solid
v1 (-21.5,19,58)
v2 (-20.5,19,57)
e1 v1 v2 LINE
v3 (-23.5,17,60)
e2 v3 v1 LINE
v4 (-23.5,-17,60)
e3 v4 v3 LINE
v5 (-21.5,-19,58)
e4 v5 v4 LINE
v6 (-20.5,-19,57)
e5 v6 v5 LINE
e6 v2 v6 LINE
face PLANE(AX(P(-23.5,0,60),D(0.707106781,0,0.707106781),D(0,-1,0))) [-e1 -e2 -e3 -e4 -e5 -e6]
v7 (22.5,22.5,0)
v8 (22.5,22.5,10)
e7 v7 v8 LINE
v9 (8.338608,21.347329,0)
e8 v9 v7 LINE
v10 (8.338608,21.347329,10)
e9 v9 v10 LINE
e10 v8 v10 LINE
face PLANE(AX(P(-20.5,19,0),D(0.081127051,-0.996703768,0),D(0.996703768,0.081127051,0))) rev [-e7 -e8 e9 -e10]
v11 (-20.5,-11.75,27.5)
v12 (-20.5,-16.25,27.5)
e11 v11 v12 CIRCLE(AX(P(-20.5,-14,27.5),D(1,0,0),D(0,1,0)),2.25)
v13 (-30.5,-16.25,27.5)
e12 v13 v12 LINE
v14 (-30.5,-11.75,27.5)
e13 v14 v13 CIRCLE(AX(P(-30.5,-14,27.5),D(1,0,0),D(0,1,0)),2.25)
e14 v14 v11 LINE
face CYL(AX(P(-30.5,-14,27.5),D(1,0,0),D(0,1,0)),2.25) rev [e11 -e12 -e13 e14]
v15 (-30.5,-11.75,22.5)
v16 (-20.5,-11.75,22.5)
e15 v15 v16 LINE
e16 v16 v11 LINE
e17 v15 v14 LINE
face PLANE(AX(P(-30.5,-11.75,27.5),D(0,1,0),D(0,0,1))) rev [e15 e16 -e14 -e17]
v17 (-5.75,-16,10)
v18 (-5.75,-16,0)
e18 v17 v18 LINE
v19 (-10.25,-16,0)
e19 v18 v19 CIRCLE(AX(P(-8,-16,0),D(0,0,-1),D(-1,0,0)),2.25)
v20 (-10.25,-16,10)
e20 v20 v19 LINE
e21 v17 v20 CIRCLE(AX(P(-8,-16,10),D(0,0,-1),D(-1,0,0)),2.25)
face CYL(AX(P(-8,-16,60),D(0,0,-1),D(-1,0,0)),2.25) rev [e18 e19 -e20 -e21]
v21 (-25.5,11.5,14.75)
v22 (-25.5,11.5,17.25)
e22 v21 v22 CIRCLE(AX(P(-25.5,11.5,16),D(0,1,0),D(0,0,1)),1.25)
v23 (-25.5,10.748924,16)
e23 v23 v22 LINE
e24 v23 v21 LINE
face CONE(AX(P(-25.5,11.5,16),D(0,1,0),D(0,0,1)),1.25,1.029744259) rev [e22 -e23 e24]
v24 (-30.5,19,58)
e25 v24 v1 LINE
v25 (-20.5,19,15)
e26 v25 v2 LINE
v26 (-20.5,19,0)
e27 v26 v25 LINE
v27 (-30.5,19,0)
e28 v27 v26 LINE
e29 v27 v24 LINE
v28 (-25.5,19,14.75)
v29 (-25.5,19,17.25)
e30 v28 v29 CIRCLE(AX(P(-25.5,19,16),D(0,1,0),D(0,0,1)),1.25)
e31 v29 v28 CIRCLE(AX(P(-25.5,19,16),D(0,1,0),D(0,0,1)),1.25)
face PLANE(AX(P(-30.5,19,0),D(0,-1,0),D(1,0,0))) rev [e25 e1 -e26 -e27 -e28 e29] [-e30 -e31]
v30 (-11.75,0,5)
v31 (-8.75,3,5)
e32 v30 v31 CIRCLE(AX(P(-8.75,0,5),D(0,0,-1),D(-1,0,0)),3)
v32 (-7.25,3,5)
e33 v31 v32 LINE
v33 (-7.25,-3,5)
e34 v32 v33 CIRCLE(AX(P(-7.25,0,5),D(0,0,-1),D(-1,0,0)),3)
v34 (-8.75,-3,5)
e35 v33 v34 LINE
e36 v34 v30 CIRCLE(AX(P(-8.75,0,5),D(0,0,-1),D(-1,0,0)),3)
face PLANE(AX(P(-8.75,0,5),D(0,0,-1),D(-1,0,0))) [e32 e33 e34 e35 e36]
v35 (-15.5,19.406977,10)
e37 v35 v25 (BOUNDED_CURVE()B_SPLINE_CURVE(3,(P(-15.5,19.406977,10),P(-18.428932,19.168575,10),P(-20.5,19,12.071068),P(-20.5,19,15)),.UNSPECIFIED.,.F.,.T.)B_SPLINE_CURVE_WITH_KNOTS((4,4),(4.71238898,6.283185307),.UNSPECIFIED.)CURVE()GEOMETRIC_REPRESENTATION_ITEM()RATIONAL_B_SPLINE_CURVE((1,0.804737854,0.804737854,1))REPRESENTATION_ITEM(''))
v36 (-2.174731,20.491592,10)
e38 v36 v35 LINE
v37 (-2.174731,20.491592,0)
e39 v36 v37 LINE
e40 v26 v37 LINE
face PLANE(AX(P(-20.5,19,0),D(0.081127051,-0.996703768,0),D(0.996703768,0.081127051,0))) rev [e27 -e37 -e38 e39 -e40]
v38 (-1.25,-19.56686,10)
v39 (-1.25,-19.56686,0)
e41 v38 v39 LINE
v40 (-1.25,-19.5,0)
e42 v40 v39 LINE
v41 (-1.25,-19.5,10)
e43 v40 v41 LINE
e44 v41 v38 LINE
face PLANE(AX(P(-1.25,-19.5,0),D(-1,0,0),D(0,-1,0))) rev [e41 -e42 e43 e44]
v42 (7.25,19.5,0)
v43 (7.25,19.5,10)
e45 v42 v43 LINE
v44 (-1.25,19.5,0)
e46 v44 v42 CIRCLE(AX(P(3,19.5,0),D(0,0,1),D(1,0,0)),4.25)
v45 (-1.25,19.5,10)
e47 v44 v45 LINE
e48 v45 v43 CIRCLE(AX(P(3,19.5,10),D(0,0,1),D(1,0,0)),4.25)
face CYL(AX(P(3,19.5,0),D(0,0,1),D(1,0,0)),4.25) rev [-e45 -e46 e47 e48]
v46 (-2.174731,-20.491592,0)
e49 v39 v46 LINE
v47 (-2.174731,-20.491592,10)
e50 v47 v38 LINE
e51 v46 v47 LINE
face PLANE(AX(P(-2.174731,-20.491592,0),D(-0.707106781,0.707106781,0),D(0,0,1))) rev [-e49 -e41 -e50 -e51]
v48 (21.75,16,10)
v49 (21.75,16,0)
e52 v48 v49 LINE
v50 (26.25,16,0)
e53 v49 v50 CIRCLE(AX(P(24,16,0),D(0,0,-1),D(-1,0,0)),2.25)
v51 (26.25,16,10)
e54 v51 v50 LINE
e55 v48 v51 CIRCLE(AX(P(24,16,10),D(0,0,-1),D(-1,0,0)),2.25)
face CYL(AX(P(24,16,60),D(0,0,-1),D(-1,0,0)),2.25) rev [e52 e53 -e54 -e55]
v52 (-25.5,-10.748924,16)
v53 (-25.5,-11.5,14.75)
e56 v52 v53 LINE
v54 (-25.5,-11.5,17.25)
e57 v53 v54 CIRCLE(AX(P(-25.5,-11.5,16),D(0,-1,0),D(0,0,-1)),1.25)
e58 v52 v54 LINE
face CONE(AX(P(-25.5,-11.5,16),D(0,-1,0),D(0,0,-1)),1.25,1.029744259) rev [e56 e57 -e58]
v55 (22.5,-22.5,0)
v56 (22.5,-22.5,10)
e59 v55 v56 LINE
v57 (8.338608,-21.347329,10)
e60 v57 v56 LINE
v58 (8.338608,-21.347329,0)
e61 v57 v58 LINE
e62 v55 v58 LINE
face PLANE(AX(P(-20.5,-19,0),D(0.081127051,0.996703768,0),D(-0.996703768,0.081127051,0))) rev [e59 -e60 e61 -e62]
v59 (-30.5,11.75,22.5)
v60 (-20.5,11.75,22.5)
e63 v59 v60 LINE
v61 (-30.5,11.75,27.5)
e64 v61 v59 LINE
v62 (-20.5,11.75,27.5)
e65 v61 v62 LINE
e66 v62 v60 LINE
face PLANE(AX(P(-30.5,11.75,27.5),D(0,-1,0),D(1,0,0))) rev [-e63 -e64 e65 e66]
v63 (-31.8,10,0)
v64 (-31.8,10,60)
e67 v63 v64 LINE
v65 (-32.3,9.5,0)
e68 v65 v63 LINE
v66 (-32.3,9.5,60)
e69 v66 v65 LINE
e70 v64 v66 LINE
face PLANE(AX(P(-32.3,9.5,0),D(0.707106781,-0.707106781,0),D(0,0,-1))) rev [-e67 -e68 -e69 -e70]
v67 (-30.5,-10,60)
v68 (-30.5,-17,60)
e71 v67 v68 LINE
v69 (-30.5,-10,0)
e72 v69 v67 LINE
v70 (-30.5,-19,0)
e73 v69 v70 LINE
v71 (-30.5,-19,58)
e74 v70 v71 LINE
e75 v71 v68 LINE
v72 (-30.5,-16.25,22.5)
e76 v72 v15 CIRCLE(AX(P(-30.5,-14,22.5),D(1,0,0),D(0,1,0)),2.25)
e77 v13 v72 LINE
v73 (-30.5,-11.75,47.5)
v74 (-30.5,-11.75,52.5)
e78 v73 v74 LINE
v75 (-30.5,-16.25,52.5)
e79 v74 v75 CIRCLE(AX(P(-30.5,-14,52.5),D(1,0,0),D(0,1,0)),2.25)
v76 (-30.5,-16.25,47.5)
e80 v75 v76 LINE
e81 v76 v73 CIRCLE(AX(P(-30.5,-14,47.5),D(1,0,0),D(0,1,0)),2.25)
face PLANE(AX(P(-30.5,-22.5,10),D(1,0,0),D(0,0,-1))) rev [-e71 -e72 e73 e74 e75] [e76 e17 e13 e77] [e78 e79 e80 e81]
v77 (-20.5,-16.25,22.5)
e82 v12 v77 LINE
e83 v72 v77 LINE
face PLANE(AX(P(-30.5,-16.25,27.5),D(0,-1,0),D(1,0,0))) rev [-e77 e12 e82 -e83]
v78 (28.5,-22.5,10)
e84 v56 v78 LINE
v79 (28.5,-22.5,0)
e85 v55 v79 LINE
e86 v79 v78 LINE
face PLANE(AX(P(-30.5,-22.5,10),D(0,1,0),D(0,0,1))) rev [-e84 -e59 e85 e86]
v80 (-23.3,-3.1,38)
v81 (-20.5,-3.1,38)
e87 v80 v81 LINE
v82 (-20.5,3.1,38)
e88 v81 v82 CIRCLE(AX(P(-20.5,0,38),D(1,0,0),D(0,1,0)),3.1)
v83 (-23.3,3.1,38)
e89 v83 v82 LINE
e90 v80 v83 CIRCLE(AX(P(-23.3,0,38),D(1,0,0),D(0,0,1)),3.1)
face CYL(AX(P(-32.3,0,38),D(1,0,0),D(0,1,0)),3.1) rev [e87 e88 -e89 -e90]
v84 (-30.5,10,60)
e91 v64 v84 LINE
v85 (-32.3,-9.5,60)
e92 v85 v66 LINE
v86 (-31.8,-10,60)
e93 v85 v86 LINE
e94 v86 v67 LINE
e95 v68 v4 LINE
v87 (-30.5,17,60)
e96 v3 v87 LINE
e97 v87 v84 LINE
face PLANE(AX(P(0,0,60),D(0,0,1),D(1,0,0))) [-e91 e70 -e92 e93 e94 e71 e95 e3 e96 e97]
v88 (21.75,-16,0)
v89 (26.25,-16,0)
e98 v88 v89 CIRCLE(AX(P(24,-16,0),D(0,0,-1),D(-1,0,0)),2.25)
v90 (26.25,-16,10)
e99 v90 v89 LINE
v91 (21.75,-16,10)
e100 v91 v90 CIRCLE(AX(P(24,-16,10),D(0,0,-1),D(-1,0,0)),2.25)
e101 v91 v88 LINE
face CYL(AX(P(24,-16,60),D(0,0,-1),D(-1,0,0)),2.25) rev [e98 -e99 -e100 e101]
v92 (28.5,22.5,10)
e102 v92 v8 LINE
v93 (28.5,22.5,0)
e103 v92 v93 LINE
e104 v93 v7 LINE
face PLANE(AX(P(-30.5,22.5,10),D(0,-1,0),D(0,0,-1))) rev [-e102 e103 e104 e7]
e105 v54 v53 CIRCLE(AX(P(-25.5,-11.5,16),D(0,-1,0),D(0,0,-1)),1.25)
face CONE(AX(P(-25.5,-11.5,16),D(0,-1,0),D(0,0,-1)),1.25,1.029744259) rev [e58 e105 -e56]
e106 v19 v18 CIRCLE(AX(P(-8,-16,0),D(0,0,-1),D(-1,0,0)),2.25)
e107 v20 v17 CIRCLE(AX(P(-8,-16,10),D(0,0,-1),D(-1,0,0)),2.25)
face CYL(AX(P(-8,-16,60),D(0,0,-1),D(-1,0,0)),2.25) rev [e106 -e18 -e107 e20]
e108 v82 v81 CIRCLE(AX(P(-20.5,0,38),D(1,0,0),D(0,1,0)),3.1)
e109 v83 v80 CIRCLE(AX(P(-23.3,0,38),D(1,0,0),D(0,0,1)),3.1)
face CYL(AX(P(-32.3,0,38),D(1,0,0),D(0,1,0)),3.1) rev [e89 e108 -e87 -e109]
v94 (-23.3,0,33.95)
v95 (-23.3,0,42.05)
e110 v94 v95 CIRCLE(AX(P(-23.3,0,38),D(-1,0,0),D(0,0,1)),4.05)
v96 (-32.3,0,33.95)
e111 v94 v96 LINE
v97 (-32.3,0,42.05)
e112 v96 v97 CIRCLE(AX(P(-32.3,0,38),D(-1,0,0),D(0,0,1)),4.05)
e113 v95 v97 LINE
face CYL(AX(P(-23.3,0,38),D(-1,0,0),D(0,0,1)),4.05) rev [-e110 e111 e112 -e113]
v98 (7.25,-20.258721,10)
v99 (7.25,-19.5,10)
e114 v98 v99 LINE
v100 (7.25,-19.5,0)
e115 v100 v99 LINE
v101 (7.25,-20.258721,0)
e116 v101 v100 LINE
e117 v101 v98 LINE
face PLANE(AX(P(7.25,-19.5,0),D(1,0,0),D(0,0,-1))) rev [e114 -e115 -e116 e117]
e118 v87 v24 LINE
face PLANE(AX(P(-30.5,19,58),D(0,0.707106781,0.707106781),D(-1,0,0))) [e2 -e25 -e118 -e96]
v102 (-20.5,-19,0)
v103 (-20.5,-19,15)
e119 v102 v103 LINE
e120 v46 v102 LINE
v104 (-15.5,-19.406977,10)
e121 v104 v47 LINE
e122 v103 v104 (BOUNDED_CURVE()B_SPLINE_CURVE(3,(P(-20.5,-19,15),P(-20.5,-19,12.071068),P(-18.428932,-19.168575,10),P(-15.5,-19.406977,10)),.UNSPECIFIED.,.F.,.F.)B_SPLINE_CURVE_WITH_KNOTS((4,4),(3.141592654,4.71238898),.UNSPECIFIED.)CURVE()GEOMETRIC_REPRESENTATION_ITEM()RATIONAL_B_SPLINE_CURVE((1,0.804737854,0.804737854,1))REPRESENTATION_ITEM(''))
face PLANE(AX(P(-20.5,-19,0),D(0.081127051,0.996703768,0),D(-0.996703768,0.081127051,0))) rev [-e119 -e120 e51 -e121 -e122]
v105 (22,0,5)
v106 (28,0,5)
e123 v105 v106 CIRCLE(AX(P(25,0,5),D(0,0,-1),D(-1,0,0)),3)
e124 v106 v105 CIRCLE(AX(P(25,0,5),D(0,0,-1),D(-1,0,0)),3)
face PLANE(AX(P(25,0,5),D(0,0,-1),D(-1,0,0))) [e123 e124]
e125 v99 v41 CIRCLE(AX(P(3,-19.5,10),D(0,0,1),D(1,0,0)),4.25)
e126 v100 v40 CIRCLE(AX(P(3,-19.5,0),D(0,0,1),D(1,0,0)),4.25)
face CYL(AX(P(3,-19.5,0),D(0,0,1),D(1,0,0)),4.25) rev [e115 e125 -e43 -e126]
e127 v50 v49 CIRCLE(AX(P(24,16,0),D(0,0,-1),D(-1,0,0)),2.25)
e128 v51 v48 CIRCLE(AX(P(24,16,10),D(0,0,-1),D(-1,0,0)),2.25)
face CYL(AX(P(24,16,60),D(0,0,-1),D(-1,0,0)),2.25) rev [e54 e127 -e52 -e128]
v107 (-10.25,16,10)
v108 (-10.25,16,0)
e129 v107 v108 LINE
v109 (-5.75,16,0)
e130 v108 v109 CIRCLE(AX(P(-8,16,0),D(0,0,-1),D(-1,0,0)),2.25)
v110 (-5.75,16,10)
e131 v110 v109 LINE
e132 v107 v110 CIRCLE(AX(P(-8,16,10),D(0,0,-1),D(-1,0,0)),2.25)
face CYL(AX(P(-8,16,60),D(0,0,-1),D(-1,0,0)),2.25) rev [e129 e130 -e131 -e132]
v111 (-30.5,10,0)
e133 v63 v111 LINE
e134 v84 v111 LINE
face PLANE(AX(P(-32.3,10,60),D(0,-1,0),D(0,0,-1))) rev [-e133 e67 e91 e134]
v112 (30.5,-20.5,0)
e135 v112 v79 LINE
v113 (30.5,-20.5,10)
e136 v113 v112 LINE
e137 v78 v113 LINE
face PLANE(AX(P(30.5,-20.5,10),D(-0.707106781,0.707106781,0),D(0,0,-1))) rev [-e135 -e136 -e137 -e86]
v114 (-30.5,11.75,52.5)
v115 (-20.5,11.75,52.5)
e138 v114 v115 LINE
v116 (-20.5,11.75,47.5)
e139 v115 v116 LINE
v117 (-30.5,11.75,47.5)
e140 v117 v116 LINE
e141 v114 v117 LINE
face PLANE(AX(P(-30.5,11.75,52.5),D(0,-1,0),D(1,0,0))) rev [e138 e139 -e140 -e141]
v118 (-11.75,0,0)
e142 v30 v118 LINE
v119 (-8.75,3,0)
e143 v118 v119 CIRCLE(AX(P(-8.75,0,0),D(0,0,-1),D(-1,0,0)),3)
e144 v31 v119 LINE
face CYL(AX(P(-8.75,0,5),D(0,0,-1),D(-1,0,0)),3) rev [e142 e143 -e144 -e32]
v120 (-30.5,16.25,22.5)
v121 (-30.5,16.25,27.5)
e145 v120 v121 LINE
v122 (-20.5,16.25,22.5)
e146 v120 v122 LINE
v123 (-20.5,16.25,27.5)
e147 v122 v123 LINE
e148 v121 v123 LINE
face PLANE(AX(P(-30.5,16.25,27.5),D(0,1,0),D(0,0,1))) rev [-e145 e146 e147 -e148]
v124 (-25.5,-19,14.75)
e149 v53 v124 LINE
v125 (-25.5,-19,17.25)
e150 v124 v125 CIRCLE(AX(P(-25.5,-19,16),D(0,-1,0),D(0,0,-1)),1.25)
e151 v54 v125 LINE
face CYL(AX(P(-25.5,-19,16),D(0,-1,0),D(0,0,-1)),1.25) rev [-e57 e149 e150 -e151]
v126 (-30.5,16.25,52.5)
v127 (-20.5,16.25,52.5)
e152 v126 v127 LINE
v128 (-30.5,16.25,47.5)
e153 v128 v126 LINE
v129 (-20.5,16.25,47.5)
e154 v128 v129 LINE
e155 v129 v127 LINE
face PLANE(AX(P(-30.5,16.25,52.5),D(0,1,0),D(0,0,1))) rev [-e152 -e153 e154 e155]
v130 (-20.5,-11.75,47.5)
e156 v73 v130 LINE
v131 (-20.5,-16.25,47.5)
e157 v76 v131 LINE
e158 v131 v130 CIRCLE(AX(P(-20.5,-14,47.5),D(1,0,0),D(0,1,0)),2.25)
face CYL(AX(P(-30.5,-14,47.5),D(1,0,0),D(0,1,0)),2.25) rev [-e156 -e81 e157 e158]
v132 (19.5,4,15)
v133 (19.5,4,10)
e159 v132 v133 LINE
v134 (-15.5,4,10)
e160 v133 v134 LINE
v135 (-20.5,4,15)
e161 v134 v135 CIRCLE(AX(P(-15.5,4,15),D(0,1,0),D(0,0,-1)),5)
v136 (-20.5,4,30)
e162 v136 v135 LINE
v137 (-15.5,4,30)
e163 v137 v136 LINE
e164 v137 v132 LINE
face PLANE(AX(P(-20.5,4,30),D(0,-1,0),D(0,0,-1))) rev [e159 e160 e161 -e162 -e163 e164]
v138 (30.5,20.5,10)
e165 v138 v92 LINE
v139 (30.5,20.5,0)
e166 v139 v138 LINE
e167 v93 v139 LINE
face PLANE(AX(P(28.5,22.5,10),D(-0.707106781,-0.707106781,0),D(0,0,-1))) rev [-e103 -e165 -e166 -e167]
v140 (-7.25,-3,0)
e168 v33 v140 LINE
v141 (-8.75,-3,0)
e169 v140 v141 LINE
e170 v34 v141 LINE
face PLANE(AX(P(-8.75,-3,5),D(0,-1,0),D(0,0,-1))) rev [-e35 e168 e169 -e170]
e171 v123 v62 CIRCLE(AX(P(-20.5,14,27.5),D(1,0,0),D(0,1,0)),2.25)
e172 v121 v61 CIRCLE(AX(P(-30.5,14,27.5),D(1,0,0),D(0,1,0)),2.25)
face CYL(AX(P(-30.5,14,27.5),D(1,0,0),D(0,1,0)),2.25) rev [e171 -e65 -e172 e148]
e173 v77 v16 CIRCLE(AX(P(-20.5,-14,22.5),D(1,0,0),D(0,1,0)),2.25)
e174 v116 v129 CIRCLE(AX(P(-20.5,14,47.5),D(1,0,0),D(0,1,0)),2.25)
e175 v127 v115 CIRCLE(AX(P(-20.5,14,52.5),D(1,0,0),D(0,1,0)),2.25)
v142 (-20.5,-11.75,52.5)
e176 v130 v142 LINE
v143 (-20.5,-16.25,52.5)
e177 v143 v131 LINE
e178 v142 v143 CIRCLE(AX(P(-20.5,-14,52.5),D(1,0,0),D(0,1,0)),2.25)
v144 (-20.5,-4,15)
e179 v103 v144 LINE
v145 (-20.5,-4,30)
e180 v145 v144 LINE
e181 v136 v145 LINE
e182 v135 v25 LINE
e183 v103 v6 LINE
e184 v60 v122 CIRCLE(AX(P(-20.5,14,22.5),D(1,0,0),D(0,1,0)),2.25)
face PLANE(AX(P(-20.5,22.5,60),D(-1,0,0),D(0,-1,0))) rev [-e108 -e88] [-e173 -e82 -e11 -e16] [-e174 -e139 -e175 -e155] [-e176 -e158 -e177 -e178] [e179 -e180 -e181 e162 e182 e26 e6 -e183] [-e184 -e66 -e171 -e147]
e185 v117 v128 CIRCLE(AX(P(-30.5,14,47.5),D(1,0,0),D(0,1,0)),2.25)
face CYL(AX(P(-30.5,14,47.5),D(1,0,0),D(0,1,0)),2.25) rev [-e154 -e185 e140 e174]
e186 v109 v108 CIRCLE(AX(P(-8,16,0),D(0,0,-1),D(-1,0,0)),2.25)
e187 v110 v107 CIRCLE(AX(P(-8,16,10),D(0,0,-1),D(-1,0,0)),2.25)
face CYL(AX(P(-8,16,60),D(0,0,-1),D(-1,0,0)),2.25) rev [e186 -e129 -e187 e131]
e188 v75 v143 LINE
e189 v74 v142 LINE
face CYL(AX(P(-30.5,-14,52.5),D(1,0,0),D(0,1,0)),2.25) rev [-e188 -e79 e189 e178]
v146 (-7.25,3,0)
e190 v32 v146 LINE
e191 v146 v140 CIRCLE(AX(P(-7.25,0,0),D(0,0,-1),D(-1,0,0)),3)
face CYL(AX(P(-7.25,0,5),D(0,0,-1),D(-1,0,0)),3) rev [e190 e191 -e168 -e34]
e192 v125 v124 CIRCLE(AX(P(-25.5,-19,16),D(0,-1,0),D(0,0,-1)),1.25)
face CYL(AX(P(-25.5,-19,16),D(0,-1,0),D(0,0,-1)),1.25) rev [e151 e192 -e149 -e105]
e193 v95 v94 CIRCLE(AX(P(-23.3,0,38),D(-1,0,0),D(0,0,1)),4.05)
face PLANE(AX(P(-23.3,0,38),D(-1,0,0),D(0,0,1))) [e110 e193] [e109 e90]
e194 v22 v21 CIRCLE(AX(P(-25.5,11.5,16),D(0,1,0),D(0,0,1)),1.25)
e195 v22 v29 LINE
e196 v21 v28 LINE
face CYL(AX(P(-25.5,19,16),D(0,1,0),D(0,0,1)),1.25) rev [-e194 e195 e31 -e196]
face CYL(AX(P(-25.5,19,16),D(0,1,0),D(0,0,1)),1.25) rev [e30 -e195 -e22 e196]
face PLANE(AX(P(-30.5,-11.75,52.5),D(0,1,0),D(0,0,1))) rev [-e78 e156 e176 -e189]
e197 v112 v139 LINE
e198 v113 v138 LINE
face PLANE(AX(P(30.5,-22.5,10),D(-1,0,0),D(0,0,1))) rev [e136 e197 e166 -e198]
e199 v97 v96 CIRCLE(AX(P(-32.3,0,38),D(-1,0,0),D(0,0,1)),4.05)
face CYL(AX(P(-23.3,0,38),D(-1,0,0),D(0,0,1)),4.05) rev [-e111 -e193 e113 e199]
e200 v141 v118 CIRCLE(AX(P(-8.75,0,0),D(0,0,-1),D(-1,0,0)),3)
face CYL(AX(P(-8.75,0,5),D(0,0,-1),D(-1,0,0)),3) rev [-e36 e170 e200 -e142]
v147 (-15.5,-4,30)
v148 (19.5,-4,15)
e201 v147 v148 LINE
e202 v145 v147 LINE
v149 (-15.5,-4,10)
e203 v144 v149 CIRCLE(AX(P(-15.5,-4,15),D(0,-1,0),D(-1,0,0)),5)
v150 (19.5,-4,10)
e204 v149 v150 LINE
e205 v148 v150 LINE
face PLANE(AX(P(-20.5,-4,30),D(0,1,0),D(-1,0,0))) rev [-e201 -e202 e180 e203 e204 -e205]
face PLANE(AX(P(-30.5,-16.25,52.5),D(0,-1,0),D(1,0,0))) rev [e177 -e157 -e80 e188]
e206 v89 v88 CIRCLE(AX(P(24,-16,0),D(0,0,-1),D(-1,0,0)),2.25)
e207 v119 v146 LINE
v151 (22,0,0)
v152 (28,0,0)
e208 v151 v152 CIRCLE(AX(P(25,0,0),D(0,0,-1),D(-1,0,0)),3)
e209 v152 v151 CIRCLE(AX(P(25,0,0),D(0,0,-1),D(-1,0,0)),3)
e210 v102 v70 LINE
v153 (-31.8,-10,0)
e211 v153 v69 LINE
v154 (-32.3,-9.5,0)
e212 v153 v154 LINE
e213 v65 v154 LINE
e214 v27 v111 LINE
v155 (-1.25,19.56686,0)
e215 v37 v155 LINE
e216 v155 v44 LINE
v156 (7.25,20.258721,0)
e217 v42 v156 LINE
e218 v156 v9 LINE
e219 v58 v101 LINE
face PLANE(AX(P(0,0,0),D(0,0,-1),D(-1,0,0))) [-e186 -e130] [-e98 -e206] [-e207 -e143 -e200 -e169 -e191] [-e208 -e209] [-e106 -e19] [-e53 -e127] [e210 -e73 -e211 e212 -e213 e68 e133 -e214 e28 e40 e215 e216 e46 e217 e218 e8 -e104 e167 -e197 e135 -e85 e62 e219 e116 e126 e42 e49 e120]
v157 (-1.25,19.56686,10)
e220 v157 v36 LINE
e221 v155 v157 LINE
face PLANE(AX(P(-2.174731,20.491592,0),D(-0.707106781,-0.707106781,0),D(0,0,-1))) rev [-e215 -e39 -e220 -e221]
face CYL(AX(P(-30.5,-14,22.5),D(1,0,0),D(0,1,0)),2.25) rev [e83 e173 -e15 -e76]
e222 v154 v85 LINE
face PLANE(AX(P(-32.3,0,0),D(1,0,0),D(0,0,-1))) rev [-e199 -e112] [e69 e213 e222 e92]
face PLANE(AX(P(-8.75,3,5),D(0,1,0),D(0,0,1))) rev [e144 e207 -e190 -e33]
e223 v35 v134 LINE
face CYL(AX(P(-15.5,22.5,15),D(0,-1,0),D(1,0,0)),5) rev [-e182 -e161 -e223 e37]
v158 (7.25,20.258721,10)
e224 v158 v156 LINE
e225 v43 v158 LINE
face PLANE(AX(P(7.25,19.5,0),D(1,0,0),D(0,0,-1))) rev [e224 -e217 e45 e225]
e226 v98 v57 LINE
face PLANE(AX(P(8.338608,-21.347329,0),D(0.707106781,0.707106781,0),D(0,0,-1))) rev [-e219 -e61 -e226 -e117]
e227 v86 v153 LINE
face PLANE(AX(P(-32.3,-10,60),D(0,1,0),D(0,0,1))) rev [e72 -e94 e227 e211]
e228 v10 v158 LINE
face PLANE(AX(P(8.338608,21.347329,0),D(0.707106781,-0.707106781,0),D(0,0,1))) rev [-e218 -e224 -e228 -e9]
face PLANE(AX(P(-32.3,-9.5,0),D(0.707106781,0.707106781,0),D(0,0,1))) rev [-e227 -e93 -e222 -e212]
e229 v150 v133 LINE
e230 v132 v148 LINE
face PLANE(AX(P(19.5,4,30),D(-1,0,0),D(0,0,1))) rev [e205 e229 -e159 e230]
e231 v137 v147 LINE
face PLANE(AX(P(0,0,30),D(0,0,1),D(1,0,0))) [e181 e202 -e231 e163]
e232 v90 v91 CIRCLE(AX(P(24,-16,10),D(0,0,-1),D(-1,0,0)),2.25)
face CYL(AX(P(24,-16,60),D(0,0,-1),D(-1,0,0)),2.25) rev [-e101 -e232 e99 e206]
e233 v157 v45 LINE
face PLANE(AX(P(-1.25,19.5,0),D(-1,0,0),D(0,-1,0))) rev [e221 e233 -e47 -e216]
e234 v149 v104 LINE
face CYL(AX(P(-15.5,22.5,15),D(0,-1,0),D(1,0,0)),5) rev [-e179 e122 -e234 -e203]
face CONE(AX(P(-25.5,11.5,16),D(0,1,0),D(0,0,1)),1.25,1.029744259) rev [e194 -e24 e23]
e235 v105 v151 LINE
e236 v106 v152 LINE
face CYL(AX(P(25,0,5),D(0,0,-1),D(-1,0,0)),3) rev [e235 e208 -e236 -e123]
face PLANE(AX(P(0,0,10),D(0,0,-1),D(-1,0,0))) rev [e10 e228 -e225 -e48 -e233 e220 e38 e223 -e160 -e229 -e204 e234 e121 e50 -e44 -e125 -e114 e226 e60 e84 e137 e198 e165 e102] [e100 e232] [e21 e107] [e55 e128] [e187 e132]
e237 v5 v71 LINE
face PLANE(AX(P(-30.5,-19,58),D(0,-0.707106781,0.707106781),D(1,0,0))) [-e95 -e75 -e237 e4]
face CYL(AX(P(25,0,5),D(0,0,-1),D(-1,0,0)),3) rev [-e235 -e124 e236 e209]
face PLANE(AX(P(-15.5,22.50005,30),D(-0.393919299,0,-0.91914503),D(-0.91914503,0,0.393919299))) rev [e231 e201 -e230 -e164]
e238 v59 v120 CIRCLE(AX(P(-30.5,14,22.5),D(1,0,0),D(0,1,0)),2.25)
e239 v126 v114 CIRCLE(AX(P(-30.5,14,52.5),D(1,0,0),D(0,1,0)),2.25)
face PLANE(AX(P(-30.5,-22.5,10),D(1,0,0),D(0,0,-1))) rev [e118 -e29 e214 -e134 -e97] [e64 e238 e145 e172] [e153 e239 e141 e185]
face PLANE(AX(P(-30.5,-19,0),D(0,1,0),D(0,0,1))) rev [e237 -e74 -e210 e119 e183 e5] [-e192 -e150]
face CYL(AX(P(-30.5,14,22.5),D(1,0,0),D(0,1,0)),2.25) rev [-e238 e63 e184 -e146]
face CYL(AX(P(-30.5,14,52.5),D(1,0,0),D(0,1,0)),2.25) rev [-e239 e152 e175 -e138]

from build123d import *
from OCP.BRepFilletAPI import BRepFilletAPI_MakeChamfer

# Parameters (mm, degrees)
SKETCH1_W            = 61
SKETCH1_H            = 45
BOSS_EXTRUDE1_DEPTH  = 10
SKETCH2_W            = 10
SKETCH2_H            = 45
BOSS_EXTRUDE2_DEPTH  = 50
CUT_EXTRUDE3_DEPTH   = 82.897802168
SKETCH6_W            = 40
SKETCH6_H            = 8
BOSS_EXTRUDE3_DEPTH  = 20
CUT_EXTRUDE4_DEPTH   = 73.336021455
FILLET1_R            = 5
CUT_EXTRUDE5_DEPTH   = 71.968302784
LPATTERN2_COUNT      = 2
LPATTERN2_PITCH      = 28
LPATTERN2_COUNT_DIR2 = 2
LPATTERN2_PITCH_DIR2 = 25
SKETCH9_R            = 3
CUT_EXTRUDE6_DEPTH   = 5
SKETCH10_R           = 2.25
CUT_EXTRUDE7_DEPTH   = 71.968302784
CHAMFER1_SIZE        = 2
SKETCH4_W            = 60
SKETCH4_H            = 20
BOSS_EXTRUDE4_DEPTH  = 1.8
CHAMFER2_SIZE        = 0.5
SKETCH15_R           = 3.1
CUT_EXTRUDE8_DEPTH   = 82.897802168
SKETCH16_R           = 4.05
CUT_EXTRUDE9_DEPTH   = 9
CUT_EXTRUDE10_DEPTH  = 10
CHAMFER3_SIZE        = 1
CHAMFER3_SIZE2       = 0.927789392
CHAMFER3_SIZE2_2     = 1.092207765
CHAMFER4_SIZE        = 3


with BuildPart() as part:
    # Sketch1 → Boss-Extrude1 (new body)
    with BuildSketch(Plane.XY):
        Rectangle(SKETCH1_W, SKETCH1_H)
    extrude(amount=BOSS_EXTRUDE1_DEPTH)

    # Sketch2 → Boss-Extrude2 (add)
    with BuildSketch(Plane.XY.offset(10)):
        with Locations((-25.5, 0)):
            Rectangle(SKETCH2_W, SKETCH2_H)
    extrude(amount=BOSS_EXTRUDE2_DEPTH)

    # Sketch5 → Cut-Extrude3 (cut, through all)
    with BuildSketch(Plane(origin=(-20.5, 0, 0), x_dir=(0, 0, -1), z_dir=(1, 0, 0))):
        with BuildLine():
            Line((-52.5, -11.75), (-47.5, -11.75))
            ThreePointArc((-47.5, -11.75), (-45.25, -14), (-47.5, -16.25))
            Line((-47.5, -16.25), (-52.5, -16.25))
            ThreePointArc((-52.5, -16.25), (-54.75, -14), (-52.5, -11.75))
        make_face()
    cut_extrude3 = extrude(amount=-CUT_EXTRUDE3_DEPTH, mode=Mode.SUBTRACT)

    # Sketch6 → Boss-Extrude3 (add)
    with BuildSketch(Plane.XY.offset(10)):
        with Locations((-0.5, 0)):
            Rectangle(SKETCH6_W, SKETCH6_H)
    extrude(amount=BOSS_EXTRUDE3_DEPTH)

    # Sketch7 → Cut-Extrude4 (cut, through all)
    with BuildSketch(Plane.XZ.offset(4)):
        Polygon((19.5, 30), (-15.5, 30), (19.5, 15), align=None)
    extrude(amount=-CUT_EXTRUDE4_DEPTH, mode=Mode.SUBTRACT)

    # Fillet1
    fillet1_edges = [part.edges().sort_by_distance(p)[0] for p in [
        (-20.5, 13.25, 10),
        (-20.5, -13.25, 10),
    ]]
    fillet(fillet1_edges, radius=FILLET1_R)

    # Sketch8 → Cut-Extrude5 (cut, through all)
    with BuildSketch(Plane.XY.offset(60)):
        Polygon((-30.5, 22.5), (22.5, 22.5), (-20.5, 19), (-30.5, 19), align=None)
        Polygon((-20.5, -19), (22.5, -22.5), (-30.5, -22.5), (-30.5, -19), align=None)
    extrude(amount=-CUT_EXTRUDE5_DEPTH, mode=Mode.SUBTRACT)

    # LPattern2: Cut-Extrude3 2 × 2
    with Locations(*[(0, i * LPATTERN2_PITCH, -j * LPATTERN2_PITCH_DIR2) for i in range(LPATTERN2_COUNT) for j in range(LPATTERN2_COUNT_DIR2) if (i, j) != (0, 0)]):
        add(cut_extrude3, mode=Mode.SUBTRACT)

    # Sketch9 → Cut-Extrude6 (cut)
    with BuildSketch(Plane(origin=(0, 0, 0), x_dir=(-1, 0, 0), z_dir=(0, 0, -1))):
        with Locations((-25, 0)):
            Circle(SKETCH9_R)
        with BuildLine():
            Line((8.75, -3), (7.25, -3))
            ThreePointArc((7.25, -3), (4.25, 0), (7.25, 3))
            Line((7.25, 3), (8.75, 3))
            ThreePointArc((8.75, 3), (11.75, 0), (8.75, -3))
        make_face()
    extrude(amount=-CUT_EXTRUDE6_DEPTH, mode=Mode.SUBTRACT)

    # Sketch10 → Cut-Extrude7 (cut, through all)
    with BuildSketch(Plane(origin=(0, 0, 0), x_dir=(-1, 0, 0), z_dir=(0, 0, -1))):
        with Locations((8, -16)):
            Circle(SKETCH10_R)
        with Locations((-24, -16)):
            Circle(SKETCH10_R)
        with Locations((-24, 16)):
            Circle(SKETCH10_R)
        with Locations((8, 16)):
            Circle(SKETCH10_R)
    extrude(amount=-CUT_EXTRUDE7_DEPTH, mode=Mode.SUBTRACT)

    # Chamfer1
    chamfer1_edges = [part.edges().sort_by_distance(p)[0] for p in [
        (30.5, -22.5, 5),
        (30.5, 22.5, 5),
        (-25.5, -19, 60),
        (-25.5, 19, 60),
    ]]
    chamfer(chamfer1_edges, length=CHAMFER1_SIZE)

    # Sketch13 → M3 Tapped Hole1 (revolve, cut)
    with BuildSketch(Plane(origin=(-25.5, 19, 16), x_dir=(0, 0, 1), z_dir=(1, 0, 0))):
        Polygon((0, 0), (0, 8.251075774), (1.25, 7.5), (1.25, 0), align=None)
    m3_tapped_hole1 = revolve(axis=Axis((-25.5, 25.35, 16), (0, -1, 0)), mode=Mode.SUBTRACT)

    # Mirror1: M3 Tapped Hole1 across plane
    add(m3_tapped_hole1.mirror(Plane.ZX), mode=Mode.SUBTRACT)

    # Sketch4 → Boss-Extrude4 (add)
    with BuildSketch(Plane.ZY.offset(30.5)):
        with Locations((30, 0)):
            Rectangle(SKETCH4_W, SKETCH4_H)
    extrude(amount=BOSS_EXTRUDE4_DEPTH)

    # Chamfer2
    chamfer2_edges = [part.edges().sort_by_distance(p)[0] for p in [
        (-32.3, 10, 30),
        (-32.3, -10, 30),
    ]]
    chamfer(chamfer2_edges, length=CHAMFER2_SIZE)

    # Sketch15 → Cut-Extrude8 (cut, through all)
    with BuildSketch(Plane(origin=(-20.5, 0, 0), x_dir=(0, 0, -1), z_dir=(1, 0, 0))):
        with Locations(Location((-38, 0, 0), (0, 0, 90))):
            Circle(SKETCH15_R)
    extrude(amount=-CUT_EXTRUDE8_DEPTH, mode=Mode.SUBTRACT)

    # Sketch16 → Cut-Extrude9 (cut)
    with BuildSketch(Plane.ZY.offset(32.3)):
        with Locations((38, 0)):
            Circle(SKETCH16_R)
    extrude(amount=-CUT_EXTRUDE9_DEPTH, mode=Mode.SUBTRACT)

    # Sketch17 → Cut-Extrude10 (cut)
    with BuildSketch(Plane.XY.offset(10)):
        with BuildLine():
            Line((7.25, -19.5), (7.25, -28.943782823))
            ThreePointArc((7.25, -28.943782823), (3, -33.193782823), (-1.25, -28.943782823))
            Line((-1.25, -28.943782823), (-1.25, -19.5))
            ThreePointArc((-1.25, -19.5), (3, -15.25), (7.25, -19.5))
        make_face()
        with BuildLine():
            Line((-1.25, 19.5), (-1.25, 28.943782823))
            ThreePointArc((-1.25, 28.943782823), (3, 33.193782823), (7.25, 28.943782823))
            Line((7.25, 28.943782823), (7.25, 19.5))
            ThreePointArc((7.25, 19.5), (3, 15.25), (-1.25, 19.5))
        make_face()
    extrude(amount=-CUT_EXTRUDE10_DEPTH, mode=Mode.SUBTRACT)

    # Chamfer3: one chamfer whose edges measure the first distance from different faces: ONE call of the kernel's chamfer builder (chamfer() names one face for all edges)
    chamfer3_edges_1 = [part.edges().sort_by_distance(p)[0] for p in [
        (-1.25, -20.566860465, 5),
    ]]
    chamfer3_side_1 = [part.faces().sort_by_distance(p)[0] for p in [
        (-1.25, -20.033430233, 5),
    ]]
    chamfer3_edges_2 = [part.edges().sort_by_distance(p)[0] for p in [
        (7.25, -21.25872093, 5),
    ]]
    chamfer3_side_2 = [part.faces().sort_by_distance(p)[0] for p in [
        (7.25, -20.379360465, 5),
    ]]
    chamfer3_edges_3 = [part.edges().sort_by_distance(p)[0] for p in [
        (7.25, 21.25872093, 5),
    ]]
    chamfer3_side_3 = [part.faces().sort_by_distance(p)[0] for p in [
        (7.25, 20.379360465, 5),
    ]]
    chamfer3_edges_4 = [part.edges().sort_by_distance(p)[0] for p in [
        (-1.25, 20.566860465, 5),
    ]]
    chamfer3_side_4 = [part.faces().sort_by_distance(p)[0] for p in [
        (-1.25, 20.033430233, 5),
    ]]
    chamfer3 = BRepFilletAPI_MakeChamfer(part.part.solid().wrapped)
    for e in chamfer3_edges_1:
        chamfer3.Add(CHAMFER3_SIZE, CHAMFER3_SIZE2, e.wrapped, chamfer3_side_1[0].wrapped)  # the first distance lies on this face
    for e in chamfer3_edges_2:
        chamfer3.Add(CHAMFER3_SIZE, CHAMFER3_SIZE2_2, e.wrapped, chamfer3_side_2[0].wrapped)  # the first distance lies on this face
    for e in chamfer3_edges_3:
        chamfer3.Add(CHAMFER3_SIZE, CHAMFER3_SIZE2_2, e.wrapped, chamfer3_side_3[0].wrapped)  # the first distance lies on this face
    for e in chamfer3_edges_4:
        chamfer3.Add(CHAMFER3_SIZE, CHAMFER3_SIZE2, e.wrapped, chamfer3_side_4[0].wrapped)  # the first distance lies on this face
    add(Compound.cast(chamfer3.Shape()), mode=Mode.REPLACE)

    # Chamfer4
    chamfer4_edges = [part.edges().sort_by_distance(p)[0] for p in [
        (-20.5, 0, 60),
    ]]
    chamfer(chamfer4_edges, length=CHAMFER4_SIZE)


solid = part.part
